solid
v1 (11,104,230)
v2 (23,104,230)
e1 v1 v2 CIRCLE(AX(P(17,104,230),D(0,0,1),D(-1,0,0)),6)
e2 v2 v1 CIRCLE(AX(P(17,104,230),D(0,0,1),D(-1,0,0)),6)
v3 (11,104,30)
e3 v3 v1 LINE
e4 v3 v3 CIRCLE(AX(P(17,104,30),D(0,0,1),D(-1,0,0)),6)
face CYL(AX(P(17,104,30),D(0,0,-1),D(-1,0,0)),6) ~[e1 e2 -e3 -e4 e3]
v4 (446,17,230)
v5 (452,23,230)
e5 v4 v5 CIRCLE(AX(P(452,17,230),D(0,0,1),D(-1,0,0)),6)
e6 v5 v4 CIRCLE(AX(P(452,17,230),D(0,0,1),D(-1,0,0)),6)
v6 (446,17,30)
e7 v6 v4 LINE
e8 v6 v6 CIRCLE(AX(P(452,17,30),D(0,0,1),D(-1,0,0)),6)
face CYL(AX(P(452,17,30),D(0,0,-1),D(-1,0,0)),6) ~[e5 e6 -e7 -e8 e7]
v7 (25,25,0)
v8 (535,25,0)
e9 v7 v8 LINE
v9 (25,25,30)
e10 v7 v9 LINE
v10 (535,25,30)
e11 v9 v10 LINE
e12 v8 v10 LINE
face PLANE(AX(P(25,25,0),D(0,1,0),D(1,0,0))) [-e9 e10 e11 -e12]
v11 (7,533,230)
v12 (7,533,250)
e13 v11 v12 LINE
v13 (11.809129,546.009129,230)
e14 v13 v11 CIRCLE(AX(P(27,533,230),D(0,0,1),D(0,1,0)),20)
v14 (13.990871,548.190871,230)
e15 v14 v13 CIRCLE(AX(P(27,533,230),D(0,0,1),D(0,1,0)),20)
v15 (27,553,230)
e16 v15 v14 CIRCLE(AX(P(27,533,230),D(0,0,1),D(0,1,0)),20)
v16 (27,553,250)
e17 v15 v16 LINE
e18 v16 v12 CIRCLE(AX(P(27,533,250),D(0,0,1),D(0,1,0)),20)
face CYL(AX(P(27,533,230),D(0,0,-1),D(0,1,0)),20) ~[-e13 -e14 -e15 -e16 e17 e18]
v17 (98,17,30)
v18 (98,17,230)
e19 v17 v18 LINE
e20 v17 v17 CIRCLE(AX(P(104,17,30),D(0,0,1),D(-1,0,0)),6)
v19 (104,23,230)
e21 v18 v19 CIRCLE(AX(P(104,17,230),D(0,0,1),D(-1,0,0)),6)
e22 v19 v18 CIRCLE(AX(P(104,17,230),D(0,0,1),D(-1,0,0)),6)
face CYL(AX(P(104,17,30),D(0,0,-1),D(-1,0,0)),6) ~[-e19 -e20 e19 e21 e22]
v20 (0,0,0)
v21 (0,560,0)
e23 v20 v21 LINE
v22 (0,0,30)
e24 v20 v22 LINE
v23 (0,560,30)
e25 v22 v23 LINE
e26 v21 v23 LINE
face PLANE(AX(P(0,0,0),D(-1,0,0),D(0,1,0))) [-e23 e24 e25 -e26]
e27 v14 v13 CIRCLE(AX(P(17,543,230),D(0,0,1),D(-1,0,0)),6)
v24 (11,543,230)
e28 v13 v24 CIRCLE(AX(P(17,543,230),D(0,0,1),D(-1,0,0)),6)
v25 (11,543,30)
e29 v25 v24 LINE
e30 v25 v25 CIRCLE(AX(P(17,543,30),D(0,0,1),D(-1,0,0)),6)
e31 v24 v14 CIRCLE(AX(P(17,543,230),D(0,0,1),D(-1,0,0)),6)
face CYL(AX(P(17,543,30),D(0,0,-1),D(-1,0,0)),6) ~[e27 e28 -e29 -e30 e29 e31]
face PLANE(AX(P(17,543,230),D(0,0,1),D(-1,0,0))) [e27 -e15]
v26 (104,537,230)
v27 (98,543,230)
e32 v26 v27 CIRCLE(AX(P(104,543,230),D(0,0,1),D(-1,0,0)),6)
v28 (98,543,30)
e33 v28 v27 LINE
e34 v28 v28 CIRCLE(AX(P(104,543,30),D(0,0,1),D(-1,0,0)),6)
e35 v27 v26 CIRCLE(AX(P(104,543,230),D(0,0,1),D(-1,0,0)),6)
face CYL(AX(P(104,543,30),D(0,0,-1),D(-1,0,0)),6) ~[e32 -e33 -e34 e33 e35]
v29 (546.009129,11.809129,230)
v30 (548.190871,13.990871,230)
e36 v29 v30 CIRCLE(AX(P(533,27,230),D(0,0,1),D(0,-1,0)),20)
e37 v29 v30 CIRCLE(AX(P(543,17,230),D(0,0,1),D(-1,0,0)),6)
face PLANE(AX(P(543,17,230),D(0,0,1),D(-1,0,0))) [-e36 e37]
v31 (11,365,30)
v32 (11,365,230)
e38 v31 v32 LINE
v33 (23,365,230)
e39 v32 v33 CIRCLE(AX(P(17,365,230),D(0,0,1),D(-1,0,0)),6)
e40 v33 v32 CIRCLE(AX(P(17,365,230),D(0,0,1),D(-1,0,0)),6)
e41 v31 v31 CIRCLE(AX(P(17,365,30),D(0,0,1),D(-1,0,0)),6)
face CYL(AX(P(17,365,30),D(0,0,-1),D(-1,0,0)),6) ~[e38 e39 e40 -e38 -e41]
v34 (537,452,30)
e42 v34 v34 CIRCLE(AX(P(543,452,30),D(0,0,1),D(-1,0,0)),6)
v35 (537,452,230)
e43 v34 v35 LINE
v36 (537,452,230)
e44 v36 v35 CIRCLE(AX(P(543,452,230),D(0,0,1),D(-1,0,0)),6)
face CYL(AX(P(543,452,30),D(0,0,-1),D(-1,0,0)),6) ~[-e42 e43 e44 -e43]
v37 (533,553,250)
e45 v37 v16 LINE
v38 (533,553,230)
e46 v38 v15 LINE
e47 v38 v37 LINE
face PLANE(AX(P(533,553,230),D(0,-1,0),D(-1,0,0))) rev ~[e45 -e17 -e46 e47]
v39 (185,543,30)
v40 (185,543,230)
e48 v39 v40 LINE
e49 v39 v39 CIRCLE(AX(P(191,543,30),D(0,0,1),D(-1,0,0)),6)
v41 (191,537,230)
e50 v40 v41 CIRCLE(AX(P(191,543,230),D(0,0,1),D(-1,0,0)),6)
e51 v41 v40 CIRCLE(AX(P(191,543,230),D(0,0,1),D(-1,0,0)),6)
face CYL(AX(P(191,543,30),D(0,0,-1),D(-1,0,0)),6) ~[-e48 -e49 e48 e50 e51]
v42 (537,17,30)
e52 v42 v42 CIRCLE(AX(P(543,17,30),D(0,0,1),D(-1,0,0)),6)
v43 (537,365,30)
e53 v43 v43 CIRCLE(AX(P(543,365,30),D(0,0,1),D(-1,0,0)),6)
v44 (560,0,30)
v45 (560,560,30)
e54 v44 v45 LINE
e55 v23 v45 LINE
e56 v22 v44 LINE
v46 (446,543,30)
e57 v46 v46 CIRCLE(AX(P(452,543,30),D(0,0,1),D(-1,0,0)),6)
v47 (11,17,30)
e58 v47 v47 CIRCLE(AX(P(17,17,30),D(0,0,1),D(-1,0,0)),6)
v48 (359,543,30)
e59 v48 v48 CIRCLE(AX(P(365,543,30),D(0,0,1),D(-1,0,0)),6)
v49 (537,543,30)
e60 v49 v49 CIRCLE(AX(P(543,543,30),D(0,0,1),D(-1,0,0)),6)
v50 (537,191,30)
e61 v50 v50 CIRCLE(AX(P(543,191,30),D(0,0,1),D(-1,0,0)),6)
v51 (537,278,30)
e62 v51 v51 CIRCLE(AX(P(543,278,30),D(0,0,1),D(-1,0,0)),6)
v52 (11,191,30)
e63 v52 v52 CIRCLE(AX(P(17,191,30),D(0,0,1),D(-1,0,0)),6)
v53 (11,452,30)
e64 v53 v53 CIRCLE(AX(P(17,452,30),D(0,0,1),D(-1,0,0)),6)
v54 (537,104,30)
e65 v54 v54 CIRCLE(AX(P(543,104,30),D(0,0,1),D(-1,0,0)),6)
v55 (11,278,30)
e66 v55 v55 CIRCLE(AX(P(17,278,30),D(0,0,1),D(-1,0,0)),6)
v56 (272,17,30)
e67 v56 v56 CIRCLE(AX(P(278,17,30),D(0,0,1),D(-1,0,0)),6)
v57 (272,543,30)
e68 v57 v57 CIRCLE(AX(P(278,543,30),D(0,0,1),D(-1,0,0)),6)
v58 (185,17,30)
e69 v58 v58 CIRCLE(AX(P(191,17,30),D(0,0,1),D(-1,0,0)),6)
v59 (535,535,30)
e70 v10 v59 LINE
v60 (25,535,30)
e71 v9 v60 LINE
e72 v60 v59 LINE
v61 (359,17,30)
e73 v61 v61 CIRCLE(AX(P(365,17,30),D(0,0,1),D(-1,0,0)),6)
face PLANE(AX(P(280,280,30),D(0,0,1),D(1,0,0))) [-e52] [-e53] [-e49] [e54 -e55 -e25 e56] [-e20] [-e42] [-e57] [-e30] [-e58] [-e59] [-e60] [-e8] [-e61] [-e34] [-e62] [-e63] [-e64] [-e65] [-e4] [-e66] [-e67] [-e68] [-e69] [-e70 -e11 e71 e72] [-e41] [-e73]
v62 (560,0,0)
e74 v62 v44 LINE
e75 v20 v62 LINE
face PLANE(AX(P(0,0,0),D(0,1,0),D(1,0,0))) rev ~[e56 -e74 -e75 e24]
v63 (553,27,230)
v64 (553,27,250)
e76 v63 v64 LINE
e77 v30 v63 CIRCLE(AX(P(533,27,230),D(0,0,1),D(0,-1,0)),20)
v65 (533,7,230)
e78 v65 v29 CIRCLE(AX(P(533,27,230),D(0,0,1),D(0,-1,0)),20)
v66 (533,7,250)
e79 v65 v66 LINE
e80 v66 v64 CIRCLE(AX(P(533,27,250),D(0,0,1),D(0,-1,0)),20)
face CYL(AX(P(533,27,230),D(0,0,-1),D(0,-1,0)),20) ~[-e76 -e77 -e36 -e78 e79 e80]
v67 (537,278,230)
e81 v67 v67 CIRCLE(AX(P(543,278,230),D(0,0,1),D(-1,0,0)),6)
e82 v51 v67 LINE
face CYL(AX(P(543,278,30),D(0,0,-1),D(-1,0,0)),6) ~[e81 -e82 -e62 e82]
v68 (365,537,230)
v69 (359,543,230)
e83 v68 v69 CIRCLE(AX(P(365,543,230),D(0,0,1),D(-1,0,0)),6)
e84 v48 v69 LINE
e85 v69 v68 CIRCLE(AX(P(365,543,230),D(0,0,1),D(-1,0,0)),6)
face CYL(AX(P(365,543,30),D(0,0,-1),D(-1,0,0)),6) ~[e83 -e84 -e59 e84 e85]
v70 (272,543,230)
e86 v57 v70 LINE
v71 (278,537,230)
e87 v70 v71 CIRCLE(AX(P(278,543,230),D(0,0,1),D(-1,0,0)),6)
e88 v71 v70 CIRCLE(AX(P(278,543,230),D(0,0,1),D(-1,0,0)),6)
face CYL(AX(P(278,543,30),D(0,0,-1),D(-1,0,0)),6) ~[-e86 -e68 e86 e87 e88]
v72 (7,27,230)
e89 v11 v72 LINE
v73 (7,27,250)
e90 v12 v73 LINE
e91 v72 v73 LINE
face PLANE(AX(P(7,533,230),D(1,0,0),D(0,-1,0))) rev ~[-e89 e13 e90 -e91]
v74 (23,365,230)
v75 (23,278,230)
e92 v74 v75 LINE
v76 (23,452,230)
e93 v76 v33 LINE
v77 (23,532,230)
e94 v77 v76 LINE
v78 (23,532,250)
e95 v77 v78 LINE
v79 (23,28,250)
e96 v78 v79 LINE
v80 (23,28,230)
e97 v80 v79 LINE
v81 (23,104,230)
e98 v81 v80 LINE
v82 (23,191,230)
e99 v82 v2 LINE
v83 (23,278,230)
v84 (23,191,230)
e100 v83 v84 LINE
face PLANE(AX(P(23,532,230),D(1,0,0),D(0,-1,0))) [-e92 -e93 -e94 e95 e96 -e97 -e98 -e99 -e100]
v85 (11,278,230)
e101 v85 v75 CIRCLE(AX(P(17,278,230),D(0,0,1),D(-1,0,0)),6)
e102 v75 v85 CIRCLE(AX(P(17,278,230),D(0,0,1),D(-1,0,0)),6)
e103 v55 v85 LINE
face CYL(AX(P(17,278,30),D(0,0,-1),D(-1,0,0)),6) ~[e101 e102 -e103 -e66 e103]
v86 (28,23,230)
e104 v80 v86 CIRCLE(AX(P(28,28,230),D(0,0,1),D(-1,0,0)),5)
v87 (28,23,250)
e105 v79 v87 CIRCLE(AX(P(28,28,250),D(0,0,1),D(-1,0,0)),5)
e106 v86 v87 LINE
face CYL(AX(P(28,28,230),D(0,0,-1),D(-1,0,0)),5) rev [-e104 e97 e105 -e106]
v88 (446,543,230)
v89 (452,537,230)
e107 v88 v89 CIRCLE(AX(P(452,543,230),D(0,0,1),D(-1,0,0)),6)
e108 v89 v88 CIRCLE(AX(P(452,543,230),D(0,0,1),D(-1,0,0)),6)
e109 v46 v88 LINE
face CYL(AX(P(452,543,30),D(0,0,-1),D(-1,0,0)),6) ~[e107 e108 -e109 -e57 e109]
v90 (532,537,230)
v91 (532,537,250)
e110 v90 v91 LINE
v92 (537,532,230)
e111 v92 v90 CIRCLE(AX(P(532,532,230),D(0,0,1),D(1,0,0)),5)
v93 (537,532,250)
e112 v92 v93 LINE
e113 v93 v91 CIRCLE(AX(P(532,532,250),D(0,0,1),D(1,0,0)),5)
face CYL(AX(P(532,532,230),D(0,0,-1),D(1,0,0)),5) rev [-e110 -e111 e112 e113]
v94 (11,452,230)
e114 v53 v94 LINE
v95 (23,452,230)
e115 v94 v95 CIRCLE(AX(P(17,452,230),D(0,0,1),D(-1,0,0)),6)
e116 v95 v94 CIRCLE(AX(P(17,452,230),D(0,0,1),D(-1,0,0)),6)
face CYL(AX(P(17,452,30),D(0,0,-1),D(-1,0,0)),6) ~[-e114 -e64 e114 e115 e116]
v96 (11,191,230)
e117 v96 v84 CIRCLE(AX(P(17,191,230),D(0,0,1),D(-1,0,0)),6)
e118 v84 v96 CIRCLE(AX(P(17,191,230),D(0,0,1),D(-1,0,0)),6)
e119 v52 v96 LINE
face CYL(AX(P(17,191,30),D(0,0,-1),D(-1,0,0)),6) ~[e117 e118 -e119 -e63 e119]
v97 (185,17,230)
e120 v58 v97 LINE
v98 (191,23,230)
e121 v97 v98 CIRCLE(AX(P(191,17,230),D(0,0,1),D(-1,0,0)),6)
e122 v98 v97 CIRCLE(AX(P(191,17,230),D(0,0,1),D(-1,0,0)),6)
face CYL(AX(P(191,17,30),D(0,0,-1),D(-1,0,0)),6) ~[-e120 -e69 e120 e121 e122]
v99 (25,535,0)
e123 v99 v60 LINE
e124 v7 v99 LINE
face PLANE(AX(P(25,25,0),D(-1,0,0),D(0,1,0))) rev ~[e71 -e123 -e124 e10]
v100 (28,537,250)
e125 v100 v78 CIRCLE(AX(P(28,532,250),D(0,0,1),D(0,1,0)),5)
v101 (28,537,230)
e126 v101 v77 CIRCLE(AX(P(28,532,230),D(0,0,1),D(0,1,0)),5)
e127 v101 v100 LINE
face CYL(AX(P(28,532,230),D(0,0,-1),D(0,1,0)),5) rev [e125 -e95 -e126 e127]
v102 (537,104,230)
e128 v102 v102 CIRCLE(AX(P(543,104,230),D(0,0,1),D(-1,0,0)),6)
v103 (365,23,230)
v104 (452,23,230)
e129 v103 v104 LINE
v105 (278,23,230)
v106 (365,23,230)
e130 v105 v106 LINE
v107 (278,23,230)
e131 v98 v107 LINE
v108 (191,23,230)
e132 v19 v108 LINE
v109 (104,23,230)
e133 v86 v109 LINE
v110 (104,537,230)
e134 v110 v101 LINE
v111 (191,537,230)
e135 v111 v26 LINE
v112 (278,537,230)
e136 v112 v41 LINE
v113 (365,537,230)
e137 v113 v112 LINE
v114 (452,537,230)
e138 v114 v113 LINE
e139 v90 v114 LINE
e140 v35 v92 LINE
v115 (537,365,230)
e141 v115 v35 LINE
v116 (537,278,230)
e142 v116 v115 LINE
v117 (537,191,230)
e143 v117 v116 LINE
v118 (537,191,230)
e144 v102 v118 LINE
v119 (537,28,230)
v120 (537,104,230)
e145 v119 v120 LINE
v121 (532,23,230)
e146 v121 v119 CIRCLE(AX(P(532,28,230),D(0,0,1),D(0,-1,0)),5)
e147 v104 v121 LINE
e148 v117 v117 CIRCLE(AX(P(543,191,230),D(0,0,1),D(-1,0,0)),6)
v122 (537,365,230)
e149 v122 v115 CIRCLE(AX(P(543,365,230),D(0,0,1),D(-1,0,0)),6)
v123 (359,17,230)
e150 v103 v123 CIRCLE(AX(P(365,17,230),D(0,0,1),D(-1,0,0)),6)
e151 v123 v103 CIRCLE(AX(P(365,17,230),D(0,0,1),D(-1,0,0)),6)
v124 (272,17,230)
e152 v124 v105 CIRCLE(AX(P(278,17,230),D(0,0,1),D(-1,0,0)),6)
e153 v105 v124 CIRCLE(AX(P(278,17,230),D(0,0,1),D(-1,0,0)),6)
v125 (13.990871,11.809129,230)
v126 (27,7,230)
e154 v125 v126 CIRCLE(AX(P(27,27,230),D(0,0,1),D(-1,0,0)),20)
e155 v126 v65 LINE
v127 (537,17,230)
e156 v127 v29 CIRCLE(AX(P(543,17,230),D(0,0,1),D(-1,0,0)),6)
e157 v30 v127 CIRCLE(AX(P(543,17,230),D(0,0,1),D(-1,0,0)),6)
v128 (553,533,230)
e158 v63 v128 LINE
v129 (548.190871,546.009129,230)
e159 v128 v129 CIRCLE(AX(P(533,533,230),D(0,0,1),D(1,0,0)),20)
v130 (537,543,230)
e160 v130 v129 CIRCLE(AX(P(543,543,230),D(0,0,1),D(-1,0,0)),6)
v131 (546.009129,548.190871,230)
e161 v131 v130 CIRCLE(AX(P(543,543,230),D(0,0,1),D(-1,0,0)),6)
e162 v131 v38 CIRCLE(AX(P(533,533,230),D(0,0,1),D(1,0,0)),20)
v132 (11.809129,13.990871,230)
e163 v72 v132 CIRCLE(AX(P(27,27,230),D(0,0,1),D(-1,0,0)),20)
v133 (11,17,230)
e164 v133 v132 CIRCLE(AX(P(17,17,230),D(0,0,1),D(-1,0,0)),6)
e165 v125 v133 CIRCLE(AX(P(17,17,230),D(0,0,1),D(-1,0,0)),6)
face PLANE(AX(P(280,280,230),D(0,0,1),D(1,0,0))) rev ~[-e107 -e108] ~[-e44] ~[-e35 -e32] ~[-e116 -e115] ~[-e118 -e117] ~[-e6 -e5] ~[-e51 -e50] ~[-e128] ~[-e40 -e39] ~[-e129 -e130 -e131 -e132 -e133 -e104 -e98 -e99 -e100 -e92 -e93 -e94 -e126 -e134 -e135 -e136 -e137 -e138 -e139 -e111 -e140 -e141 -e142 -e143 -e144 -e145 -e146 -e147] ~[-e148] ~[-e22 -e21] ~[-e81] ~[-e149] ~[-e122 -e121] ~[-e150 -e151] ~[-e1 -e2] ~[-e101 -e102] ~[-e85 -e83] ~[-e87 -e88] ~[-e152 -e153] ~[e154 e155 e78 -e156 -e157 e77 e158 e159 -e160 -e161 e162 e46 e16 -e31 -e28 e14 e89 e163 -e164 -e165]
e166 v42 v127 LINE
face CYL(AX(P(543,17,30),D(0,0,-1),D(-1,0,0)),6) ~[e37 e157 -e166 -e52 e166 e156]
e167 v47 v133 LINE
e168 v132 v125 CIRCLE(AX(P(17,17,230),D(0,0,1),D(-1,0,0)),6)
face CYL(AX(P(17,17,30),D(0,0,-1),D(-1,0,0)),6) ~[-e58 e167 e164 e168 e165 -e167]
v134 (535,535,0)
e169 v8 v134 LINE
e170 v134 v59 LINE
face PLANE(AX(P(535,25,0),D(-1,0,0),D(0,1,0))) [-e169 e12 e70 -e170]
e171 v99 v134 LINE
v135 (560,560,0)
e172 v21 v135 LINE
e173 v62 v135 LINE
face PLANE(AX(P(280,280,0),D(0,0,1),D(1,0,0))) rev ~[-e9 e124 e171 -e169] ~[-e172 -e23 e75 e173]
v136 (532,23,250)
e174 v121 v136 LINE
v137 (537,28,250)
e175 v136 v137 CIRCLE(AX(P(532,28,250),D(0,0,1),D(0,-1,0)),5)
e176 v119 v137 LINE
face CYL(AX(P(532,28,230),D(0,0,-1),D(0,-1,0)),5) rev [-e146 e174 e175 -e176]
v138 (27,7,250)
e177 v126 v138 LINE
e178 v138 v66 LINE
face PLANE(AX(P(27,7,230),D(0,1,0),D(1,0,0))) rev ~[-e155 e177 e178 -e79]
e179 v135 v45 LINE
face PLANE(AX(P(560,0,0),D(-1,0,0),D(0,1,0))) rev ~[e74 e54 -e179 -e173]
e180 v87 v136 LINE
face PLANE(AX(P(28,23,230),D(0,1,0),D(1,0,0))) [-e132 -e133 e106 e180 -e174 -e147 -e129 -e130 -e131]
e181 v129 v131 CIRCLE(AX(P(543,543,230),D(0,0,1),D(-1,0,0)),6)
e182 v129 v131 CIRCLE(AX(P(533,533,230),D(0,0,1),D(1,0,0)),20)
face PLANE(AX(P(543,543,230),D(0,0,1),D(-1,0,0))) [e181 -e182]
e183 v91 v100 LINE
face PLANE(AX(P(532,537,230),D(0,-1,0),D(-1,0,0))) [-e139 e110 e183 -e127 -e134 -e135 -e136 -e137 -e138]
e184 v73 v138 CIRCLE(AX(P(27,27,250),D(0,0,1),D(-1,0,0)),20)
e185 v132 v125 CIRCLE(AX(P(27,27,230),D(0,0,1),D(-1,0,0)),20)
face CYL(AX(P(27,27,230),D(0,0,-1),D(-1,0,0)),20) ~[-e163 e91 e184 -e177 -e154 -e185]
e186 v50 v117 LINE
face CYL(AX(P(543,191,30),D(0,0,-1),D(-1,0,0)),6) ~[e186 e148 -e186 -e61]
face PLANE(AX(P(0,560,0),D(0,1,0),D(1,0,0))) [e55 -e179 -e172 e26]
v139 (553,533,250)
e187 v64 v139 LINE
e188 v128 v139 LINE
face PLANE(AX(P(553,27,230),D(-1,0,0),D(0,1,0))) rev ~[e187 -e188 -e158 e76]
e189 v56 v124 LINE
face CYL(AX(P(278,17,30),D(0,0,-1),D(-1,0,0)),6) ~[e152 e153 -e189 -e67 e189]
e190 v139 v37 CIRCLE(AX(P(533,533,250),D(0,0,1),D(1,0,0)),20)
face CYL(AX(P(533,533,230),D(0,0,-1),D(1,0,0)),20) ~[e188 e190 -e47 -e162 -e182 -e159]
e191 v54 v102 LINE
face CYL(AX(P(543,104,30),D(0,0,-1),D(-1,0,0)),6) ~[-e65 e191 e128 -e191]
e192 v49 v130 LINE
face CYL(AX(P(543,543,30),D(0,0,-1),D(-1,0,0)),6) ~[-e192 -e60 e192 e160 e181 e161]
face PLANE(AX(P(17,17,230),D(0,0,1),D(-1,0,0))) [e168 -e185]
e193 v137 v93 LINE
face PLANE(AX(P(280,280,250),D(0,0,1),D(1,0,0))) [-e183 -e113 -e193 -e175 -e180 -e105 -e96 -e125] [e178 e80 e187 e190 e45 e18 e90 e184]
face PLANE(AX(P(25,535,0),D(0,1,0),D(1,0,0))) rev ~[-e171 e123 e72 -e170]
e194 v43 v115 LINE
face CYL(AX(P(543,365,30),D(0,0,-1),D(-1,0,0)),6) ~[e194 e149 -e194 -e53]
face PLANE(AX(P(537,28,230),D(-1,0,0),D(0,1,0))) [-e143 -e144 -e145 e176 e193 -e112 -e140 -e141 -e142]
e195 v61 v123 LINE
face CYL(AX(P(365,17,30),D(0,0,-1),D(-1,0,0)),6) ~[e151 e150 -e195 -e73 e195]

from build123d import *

# Parameters (mm, degrees)
SKETCH1_W           = 560
SKETCH1_H           = 560
SKETCH1_W_2         = 510
SKETCH1_H_2         = 510
BOSS_EXTRUDE1_DEPTH = 30
SKETCH2_R           = 6
BOSS_EXTRUDE2_DEPTH = 200
BOSS_EXTRUDE3_DEPTH = 20


with BuildPart() as part:
    # Sketch1 → Boss-Extrude1 (new body)
    with BuildSketch(Plane.XY):
        with Locations((280, 280)):
            Rectangle(SKETCH1_W, SKETCH1_H)
        with Locations((280, 280)):
            Rectangle(SKETCH1_W_2, SKETCH1_H_2, mode=Mode.SUBTRACT)
    extrude(amount=BOSS_EXTRUDE1_DEPTH)

    # Sketch2 → Boss-Extrude2 (add)
    with BuildSketch(Plane.XY.offset(30)):
        with Locations(Location((17, 543, 0), (0, 0, 180))):
            Circle(SKETCH2_R)
        with Locations(Location((17, 17, 0), (0, 0, 180))):
            Circle(SKETCH2_R)
        with Locations(Location((543, 17, 0), (0, 0, 180))):
            Circle(SKETCH2_R)
        with Locations(Location((543, 543, 0), (0, 0, 180))):
            Circle(SKETCH2_R)
        with Locations(Location((104, 543, 0), (0, 0, 180))):
            Circle(SKETCH2_R)
        with Locations(Location((104, 17, 0), (0, 0, 180))):
            Circle(SKETCH2_R)
        with Locations(Location((191, 543, 0), (0, 0, 180))):
            Circle(SKETCH2_R)
        with Locations(Location((191, 17, 0), (0, 0, 180))):
            Circle(SKETCH2_R)
        with Locations(Location((278, 543, 0), (0, 0, 180))):
            Circle(SKETCH2_R)
        with Locations(Location((278, 17, 0), (0, 0, 180))):
            Circle(SKETCH2_R)
        with Locations(Location((365, 543, 0), (0, 0, 180))):
            Circle(SKETCH2_R)
        with Locations(Location((365, 17, 0), (0, 0, 180))):
            Circle(SKETCH2_R)
        with Locations(Location((452, 543, 0), (0, 0, 180))):
            Circle(SKETCH2_R)
        with Locations(Location((452, 17, 0), (0, 0, 180))):
            Circle(SKETCH2_R)
        with Locations(Location((17, 104, 0), (0, 0, 180))):
            Circle(SKETCH2_R)
        with Locations(Location((543, 104, 0), (0, 0, 180))):
            Circle(SKETCH2_R)
        with Locations(Location((17, 191, 0), (0, 0, 180))):
            Circle(SKETCH2_R)
        with Locations(Location((543, 191, 0), (0, 0, 180))):
            Circle(SKETCH2_R)
        with Locations(Location((17, 278, 0), (0, 0, 180))):
            Circle(SKETCH2_R)
        with Locations(Location((543, 278, 0), (0, 0, 180))):
            Circle(SKETCH2_R)
        with Locations(Location((17, 365, 0), (0, 0, 180))):
            Circle(SKETCH2_R)
        with Locations(Location((543, 365, 0), (0, 0, 180))):
            Circle(SKETCH2_R)
        with Locations(Location((17, 452, 0), (0, 0, 180))):
            Circle(SKETCH2_R)
        with Locations(Location((543, 452, 0), (0, 0, 180))):
            Circle(SKETCH2_R)
    extrude(amount=BOSS_EXTRUDE2_DEPTH)

    # Sketch3 → Boss-Extrude3 (add)
    with BuildSketch(Plane.XY.offset(230)):
        with BuildLine():
            Line((7, 533), (7, 27))
            ThreePointArc((7, 27), (12.857864376, 12.857864376), (27, 7))
            Line((27, 7), (533, 7))
            ThreePointArc((533, 7), (547.142135624, 12.857864376), (553, 27))
            Line((553, 27), (553, 533))
            ThreePointArc((553, 533), (547.142135624, 547.142135624), (533, 553))
            Line((533, 553), (27, 553))
            ThreePointArc((27, 553), (12.857864376, 547.142135624), (7, 533))
        make_face()
        with BuildLine():
            Line((23, 532), (23, 28))
            ThreePointArc((23, 28), (24.464466094, 24.464466094), (28, 23))
            Line((28, 23), (532, 23))
            ThreePointArc((532, 23), (535.535533906, 24.464466094), (537, 28))
            Line((537, 28), (537, 532))
            ThreePointArc((537, 532), (535.535533906, 535.535533906), (532, 537))
            Line((532, 537), (28, 537))
            ThreePointArc((28, 537), (24.464466094, 535.535533906), (23, 532))
        make_face(mode=Mode.SUBTRACT)
    extrude(amount=BOSS_EXTRUDE3_DEPTH)


solid = part.part
